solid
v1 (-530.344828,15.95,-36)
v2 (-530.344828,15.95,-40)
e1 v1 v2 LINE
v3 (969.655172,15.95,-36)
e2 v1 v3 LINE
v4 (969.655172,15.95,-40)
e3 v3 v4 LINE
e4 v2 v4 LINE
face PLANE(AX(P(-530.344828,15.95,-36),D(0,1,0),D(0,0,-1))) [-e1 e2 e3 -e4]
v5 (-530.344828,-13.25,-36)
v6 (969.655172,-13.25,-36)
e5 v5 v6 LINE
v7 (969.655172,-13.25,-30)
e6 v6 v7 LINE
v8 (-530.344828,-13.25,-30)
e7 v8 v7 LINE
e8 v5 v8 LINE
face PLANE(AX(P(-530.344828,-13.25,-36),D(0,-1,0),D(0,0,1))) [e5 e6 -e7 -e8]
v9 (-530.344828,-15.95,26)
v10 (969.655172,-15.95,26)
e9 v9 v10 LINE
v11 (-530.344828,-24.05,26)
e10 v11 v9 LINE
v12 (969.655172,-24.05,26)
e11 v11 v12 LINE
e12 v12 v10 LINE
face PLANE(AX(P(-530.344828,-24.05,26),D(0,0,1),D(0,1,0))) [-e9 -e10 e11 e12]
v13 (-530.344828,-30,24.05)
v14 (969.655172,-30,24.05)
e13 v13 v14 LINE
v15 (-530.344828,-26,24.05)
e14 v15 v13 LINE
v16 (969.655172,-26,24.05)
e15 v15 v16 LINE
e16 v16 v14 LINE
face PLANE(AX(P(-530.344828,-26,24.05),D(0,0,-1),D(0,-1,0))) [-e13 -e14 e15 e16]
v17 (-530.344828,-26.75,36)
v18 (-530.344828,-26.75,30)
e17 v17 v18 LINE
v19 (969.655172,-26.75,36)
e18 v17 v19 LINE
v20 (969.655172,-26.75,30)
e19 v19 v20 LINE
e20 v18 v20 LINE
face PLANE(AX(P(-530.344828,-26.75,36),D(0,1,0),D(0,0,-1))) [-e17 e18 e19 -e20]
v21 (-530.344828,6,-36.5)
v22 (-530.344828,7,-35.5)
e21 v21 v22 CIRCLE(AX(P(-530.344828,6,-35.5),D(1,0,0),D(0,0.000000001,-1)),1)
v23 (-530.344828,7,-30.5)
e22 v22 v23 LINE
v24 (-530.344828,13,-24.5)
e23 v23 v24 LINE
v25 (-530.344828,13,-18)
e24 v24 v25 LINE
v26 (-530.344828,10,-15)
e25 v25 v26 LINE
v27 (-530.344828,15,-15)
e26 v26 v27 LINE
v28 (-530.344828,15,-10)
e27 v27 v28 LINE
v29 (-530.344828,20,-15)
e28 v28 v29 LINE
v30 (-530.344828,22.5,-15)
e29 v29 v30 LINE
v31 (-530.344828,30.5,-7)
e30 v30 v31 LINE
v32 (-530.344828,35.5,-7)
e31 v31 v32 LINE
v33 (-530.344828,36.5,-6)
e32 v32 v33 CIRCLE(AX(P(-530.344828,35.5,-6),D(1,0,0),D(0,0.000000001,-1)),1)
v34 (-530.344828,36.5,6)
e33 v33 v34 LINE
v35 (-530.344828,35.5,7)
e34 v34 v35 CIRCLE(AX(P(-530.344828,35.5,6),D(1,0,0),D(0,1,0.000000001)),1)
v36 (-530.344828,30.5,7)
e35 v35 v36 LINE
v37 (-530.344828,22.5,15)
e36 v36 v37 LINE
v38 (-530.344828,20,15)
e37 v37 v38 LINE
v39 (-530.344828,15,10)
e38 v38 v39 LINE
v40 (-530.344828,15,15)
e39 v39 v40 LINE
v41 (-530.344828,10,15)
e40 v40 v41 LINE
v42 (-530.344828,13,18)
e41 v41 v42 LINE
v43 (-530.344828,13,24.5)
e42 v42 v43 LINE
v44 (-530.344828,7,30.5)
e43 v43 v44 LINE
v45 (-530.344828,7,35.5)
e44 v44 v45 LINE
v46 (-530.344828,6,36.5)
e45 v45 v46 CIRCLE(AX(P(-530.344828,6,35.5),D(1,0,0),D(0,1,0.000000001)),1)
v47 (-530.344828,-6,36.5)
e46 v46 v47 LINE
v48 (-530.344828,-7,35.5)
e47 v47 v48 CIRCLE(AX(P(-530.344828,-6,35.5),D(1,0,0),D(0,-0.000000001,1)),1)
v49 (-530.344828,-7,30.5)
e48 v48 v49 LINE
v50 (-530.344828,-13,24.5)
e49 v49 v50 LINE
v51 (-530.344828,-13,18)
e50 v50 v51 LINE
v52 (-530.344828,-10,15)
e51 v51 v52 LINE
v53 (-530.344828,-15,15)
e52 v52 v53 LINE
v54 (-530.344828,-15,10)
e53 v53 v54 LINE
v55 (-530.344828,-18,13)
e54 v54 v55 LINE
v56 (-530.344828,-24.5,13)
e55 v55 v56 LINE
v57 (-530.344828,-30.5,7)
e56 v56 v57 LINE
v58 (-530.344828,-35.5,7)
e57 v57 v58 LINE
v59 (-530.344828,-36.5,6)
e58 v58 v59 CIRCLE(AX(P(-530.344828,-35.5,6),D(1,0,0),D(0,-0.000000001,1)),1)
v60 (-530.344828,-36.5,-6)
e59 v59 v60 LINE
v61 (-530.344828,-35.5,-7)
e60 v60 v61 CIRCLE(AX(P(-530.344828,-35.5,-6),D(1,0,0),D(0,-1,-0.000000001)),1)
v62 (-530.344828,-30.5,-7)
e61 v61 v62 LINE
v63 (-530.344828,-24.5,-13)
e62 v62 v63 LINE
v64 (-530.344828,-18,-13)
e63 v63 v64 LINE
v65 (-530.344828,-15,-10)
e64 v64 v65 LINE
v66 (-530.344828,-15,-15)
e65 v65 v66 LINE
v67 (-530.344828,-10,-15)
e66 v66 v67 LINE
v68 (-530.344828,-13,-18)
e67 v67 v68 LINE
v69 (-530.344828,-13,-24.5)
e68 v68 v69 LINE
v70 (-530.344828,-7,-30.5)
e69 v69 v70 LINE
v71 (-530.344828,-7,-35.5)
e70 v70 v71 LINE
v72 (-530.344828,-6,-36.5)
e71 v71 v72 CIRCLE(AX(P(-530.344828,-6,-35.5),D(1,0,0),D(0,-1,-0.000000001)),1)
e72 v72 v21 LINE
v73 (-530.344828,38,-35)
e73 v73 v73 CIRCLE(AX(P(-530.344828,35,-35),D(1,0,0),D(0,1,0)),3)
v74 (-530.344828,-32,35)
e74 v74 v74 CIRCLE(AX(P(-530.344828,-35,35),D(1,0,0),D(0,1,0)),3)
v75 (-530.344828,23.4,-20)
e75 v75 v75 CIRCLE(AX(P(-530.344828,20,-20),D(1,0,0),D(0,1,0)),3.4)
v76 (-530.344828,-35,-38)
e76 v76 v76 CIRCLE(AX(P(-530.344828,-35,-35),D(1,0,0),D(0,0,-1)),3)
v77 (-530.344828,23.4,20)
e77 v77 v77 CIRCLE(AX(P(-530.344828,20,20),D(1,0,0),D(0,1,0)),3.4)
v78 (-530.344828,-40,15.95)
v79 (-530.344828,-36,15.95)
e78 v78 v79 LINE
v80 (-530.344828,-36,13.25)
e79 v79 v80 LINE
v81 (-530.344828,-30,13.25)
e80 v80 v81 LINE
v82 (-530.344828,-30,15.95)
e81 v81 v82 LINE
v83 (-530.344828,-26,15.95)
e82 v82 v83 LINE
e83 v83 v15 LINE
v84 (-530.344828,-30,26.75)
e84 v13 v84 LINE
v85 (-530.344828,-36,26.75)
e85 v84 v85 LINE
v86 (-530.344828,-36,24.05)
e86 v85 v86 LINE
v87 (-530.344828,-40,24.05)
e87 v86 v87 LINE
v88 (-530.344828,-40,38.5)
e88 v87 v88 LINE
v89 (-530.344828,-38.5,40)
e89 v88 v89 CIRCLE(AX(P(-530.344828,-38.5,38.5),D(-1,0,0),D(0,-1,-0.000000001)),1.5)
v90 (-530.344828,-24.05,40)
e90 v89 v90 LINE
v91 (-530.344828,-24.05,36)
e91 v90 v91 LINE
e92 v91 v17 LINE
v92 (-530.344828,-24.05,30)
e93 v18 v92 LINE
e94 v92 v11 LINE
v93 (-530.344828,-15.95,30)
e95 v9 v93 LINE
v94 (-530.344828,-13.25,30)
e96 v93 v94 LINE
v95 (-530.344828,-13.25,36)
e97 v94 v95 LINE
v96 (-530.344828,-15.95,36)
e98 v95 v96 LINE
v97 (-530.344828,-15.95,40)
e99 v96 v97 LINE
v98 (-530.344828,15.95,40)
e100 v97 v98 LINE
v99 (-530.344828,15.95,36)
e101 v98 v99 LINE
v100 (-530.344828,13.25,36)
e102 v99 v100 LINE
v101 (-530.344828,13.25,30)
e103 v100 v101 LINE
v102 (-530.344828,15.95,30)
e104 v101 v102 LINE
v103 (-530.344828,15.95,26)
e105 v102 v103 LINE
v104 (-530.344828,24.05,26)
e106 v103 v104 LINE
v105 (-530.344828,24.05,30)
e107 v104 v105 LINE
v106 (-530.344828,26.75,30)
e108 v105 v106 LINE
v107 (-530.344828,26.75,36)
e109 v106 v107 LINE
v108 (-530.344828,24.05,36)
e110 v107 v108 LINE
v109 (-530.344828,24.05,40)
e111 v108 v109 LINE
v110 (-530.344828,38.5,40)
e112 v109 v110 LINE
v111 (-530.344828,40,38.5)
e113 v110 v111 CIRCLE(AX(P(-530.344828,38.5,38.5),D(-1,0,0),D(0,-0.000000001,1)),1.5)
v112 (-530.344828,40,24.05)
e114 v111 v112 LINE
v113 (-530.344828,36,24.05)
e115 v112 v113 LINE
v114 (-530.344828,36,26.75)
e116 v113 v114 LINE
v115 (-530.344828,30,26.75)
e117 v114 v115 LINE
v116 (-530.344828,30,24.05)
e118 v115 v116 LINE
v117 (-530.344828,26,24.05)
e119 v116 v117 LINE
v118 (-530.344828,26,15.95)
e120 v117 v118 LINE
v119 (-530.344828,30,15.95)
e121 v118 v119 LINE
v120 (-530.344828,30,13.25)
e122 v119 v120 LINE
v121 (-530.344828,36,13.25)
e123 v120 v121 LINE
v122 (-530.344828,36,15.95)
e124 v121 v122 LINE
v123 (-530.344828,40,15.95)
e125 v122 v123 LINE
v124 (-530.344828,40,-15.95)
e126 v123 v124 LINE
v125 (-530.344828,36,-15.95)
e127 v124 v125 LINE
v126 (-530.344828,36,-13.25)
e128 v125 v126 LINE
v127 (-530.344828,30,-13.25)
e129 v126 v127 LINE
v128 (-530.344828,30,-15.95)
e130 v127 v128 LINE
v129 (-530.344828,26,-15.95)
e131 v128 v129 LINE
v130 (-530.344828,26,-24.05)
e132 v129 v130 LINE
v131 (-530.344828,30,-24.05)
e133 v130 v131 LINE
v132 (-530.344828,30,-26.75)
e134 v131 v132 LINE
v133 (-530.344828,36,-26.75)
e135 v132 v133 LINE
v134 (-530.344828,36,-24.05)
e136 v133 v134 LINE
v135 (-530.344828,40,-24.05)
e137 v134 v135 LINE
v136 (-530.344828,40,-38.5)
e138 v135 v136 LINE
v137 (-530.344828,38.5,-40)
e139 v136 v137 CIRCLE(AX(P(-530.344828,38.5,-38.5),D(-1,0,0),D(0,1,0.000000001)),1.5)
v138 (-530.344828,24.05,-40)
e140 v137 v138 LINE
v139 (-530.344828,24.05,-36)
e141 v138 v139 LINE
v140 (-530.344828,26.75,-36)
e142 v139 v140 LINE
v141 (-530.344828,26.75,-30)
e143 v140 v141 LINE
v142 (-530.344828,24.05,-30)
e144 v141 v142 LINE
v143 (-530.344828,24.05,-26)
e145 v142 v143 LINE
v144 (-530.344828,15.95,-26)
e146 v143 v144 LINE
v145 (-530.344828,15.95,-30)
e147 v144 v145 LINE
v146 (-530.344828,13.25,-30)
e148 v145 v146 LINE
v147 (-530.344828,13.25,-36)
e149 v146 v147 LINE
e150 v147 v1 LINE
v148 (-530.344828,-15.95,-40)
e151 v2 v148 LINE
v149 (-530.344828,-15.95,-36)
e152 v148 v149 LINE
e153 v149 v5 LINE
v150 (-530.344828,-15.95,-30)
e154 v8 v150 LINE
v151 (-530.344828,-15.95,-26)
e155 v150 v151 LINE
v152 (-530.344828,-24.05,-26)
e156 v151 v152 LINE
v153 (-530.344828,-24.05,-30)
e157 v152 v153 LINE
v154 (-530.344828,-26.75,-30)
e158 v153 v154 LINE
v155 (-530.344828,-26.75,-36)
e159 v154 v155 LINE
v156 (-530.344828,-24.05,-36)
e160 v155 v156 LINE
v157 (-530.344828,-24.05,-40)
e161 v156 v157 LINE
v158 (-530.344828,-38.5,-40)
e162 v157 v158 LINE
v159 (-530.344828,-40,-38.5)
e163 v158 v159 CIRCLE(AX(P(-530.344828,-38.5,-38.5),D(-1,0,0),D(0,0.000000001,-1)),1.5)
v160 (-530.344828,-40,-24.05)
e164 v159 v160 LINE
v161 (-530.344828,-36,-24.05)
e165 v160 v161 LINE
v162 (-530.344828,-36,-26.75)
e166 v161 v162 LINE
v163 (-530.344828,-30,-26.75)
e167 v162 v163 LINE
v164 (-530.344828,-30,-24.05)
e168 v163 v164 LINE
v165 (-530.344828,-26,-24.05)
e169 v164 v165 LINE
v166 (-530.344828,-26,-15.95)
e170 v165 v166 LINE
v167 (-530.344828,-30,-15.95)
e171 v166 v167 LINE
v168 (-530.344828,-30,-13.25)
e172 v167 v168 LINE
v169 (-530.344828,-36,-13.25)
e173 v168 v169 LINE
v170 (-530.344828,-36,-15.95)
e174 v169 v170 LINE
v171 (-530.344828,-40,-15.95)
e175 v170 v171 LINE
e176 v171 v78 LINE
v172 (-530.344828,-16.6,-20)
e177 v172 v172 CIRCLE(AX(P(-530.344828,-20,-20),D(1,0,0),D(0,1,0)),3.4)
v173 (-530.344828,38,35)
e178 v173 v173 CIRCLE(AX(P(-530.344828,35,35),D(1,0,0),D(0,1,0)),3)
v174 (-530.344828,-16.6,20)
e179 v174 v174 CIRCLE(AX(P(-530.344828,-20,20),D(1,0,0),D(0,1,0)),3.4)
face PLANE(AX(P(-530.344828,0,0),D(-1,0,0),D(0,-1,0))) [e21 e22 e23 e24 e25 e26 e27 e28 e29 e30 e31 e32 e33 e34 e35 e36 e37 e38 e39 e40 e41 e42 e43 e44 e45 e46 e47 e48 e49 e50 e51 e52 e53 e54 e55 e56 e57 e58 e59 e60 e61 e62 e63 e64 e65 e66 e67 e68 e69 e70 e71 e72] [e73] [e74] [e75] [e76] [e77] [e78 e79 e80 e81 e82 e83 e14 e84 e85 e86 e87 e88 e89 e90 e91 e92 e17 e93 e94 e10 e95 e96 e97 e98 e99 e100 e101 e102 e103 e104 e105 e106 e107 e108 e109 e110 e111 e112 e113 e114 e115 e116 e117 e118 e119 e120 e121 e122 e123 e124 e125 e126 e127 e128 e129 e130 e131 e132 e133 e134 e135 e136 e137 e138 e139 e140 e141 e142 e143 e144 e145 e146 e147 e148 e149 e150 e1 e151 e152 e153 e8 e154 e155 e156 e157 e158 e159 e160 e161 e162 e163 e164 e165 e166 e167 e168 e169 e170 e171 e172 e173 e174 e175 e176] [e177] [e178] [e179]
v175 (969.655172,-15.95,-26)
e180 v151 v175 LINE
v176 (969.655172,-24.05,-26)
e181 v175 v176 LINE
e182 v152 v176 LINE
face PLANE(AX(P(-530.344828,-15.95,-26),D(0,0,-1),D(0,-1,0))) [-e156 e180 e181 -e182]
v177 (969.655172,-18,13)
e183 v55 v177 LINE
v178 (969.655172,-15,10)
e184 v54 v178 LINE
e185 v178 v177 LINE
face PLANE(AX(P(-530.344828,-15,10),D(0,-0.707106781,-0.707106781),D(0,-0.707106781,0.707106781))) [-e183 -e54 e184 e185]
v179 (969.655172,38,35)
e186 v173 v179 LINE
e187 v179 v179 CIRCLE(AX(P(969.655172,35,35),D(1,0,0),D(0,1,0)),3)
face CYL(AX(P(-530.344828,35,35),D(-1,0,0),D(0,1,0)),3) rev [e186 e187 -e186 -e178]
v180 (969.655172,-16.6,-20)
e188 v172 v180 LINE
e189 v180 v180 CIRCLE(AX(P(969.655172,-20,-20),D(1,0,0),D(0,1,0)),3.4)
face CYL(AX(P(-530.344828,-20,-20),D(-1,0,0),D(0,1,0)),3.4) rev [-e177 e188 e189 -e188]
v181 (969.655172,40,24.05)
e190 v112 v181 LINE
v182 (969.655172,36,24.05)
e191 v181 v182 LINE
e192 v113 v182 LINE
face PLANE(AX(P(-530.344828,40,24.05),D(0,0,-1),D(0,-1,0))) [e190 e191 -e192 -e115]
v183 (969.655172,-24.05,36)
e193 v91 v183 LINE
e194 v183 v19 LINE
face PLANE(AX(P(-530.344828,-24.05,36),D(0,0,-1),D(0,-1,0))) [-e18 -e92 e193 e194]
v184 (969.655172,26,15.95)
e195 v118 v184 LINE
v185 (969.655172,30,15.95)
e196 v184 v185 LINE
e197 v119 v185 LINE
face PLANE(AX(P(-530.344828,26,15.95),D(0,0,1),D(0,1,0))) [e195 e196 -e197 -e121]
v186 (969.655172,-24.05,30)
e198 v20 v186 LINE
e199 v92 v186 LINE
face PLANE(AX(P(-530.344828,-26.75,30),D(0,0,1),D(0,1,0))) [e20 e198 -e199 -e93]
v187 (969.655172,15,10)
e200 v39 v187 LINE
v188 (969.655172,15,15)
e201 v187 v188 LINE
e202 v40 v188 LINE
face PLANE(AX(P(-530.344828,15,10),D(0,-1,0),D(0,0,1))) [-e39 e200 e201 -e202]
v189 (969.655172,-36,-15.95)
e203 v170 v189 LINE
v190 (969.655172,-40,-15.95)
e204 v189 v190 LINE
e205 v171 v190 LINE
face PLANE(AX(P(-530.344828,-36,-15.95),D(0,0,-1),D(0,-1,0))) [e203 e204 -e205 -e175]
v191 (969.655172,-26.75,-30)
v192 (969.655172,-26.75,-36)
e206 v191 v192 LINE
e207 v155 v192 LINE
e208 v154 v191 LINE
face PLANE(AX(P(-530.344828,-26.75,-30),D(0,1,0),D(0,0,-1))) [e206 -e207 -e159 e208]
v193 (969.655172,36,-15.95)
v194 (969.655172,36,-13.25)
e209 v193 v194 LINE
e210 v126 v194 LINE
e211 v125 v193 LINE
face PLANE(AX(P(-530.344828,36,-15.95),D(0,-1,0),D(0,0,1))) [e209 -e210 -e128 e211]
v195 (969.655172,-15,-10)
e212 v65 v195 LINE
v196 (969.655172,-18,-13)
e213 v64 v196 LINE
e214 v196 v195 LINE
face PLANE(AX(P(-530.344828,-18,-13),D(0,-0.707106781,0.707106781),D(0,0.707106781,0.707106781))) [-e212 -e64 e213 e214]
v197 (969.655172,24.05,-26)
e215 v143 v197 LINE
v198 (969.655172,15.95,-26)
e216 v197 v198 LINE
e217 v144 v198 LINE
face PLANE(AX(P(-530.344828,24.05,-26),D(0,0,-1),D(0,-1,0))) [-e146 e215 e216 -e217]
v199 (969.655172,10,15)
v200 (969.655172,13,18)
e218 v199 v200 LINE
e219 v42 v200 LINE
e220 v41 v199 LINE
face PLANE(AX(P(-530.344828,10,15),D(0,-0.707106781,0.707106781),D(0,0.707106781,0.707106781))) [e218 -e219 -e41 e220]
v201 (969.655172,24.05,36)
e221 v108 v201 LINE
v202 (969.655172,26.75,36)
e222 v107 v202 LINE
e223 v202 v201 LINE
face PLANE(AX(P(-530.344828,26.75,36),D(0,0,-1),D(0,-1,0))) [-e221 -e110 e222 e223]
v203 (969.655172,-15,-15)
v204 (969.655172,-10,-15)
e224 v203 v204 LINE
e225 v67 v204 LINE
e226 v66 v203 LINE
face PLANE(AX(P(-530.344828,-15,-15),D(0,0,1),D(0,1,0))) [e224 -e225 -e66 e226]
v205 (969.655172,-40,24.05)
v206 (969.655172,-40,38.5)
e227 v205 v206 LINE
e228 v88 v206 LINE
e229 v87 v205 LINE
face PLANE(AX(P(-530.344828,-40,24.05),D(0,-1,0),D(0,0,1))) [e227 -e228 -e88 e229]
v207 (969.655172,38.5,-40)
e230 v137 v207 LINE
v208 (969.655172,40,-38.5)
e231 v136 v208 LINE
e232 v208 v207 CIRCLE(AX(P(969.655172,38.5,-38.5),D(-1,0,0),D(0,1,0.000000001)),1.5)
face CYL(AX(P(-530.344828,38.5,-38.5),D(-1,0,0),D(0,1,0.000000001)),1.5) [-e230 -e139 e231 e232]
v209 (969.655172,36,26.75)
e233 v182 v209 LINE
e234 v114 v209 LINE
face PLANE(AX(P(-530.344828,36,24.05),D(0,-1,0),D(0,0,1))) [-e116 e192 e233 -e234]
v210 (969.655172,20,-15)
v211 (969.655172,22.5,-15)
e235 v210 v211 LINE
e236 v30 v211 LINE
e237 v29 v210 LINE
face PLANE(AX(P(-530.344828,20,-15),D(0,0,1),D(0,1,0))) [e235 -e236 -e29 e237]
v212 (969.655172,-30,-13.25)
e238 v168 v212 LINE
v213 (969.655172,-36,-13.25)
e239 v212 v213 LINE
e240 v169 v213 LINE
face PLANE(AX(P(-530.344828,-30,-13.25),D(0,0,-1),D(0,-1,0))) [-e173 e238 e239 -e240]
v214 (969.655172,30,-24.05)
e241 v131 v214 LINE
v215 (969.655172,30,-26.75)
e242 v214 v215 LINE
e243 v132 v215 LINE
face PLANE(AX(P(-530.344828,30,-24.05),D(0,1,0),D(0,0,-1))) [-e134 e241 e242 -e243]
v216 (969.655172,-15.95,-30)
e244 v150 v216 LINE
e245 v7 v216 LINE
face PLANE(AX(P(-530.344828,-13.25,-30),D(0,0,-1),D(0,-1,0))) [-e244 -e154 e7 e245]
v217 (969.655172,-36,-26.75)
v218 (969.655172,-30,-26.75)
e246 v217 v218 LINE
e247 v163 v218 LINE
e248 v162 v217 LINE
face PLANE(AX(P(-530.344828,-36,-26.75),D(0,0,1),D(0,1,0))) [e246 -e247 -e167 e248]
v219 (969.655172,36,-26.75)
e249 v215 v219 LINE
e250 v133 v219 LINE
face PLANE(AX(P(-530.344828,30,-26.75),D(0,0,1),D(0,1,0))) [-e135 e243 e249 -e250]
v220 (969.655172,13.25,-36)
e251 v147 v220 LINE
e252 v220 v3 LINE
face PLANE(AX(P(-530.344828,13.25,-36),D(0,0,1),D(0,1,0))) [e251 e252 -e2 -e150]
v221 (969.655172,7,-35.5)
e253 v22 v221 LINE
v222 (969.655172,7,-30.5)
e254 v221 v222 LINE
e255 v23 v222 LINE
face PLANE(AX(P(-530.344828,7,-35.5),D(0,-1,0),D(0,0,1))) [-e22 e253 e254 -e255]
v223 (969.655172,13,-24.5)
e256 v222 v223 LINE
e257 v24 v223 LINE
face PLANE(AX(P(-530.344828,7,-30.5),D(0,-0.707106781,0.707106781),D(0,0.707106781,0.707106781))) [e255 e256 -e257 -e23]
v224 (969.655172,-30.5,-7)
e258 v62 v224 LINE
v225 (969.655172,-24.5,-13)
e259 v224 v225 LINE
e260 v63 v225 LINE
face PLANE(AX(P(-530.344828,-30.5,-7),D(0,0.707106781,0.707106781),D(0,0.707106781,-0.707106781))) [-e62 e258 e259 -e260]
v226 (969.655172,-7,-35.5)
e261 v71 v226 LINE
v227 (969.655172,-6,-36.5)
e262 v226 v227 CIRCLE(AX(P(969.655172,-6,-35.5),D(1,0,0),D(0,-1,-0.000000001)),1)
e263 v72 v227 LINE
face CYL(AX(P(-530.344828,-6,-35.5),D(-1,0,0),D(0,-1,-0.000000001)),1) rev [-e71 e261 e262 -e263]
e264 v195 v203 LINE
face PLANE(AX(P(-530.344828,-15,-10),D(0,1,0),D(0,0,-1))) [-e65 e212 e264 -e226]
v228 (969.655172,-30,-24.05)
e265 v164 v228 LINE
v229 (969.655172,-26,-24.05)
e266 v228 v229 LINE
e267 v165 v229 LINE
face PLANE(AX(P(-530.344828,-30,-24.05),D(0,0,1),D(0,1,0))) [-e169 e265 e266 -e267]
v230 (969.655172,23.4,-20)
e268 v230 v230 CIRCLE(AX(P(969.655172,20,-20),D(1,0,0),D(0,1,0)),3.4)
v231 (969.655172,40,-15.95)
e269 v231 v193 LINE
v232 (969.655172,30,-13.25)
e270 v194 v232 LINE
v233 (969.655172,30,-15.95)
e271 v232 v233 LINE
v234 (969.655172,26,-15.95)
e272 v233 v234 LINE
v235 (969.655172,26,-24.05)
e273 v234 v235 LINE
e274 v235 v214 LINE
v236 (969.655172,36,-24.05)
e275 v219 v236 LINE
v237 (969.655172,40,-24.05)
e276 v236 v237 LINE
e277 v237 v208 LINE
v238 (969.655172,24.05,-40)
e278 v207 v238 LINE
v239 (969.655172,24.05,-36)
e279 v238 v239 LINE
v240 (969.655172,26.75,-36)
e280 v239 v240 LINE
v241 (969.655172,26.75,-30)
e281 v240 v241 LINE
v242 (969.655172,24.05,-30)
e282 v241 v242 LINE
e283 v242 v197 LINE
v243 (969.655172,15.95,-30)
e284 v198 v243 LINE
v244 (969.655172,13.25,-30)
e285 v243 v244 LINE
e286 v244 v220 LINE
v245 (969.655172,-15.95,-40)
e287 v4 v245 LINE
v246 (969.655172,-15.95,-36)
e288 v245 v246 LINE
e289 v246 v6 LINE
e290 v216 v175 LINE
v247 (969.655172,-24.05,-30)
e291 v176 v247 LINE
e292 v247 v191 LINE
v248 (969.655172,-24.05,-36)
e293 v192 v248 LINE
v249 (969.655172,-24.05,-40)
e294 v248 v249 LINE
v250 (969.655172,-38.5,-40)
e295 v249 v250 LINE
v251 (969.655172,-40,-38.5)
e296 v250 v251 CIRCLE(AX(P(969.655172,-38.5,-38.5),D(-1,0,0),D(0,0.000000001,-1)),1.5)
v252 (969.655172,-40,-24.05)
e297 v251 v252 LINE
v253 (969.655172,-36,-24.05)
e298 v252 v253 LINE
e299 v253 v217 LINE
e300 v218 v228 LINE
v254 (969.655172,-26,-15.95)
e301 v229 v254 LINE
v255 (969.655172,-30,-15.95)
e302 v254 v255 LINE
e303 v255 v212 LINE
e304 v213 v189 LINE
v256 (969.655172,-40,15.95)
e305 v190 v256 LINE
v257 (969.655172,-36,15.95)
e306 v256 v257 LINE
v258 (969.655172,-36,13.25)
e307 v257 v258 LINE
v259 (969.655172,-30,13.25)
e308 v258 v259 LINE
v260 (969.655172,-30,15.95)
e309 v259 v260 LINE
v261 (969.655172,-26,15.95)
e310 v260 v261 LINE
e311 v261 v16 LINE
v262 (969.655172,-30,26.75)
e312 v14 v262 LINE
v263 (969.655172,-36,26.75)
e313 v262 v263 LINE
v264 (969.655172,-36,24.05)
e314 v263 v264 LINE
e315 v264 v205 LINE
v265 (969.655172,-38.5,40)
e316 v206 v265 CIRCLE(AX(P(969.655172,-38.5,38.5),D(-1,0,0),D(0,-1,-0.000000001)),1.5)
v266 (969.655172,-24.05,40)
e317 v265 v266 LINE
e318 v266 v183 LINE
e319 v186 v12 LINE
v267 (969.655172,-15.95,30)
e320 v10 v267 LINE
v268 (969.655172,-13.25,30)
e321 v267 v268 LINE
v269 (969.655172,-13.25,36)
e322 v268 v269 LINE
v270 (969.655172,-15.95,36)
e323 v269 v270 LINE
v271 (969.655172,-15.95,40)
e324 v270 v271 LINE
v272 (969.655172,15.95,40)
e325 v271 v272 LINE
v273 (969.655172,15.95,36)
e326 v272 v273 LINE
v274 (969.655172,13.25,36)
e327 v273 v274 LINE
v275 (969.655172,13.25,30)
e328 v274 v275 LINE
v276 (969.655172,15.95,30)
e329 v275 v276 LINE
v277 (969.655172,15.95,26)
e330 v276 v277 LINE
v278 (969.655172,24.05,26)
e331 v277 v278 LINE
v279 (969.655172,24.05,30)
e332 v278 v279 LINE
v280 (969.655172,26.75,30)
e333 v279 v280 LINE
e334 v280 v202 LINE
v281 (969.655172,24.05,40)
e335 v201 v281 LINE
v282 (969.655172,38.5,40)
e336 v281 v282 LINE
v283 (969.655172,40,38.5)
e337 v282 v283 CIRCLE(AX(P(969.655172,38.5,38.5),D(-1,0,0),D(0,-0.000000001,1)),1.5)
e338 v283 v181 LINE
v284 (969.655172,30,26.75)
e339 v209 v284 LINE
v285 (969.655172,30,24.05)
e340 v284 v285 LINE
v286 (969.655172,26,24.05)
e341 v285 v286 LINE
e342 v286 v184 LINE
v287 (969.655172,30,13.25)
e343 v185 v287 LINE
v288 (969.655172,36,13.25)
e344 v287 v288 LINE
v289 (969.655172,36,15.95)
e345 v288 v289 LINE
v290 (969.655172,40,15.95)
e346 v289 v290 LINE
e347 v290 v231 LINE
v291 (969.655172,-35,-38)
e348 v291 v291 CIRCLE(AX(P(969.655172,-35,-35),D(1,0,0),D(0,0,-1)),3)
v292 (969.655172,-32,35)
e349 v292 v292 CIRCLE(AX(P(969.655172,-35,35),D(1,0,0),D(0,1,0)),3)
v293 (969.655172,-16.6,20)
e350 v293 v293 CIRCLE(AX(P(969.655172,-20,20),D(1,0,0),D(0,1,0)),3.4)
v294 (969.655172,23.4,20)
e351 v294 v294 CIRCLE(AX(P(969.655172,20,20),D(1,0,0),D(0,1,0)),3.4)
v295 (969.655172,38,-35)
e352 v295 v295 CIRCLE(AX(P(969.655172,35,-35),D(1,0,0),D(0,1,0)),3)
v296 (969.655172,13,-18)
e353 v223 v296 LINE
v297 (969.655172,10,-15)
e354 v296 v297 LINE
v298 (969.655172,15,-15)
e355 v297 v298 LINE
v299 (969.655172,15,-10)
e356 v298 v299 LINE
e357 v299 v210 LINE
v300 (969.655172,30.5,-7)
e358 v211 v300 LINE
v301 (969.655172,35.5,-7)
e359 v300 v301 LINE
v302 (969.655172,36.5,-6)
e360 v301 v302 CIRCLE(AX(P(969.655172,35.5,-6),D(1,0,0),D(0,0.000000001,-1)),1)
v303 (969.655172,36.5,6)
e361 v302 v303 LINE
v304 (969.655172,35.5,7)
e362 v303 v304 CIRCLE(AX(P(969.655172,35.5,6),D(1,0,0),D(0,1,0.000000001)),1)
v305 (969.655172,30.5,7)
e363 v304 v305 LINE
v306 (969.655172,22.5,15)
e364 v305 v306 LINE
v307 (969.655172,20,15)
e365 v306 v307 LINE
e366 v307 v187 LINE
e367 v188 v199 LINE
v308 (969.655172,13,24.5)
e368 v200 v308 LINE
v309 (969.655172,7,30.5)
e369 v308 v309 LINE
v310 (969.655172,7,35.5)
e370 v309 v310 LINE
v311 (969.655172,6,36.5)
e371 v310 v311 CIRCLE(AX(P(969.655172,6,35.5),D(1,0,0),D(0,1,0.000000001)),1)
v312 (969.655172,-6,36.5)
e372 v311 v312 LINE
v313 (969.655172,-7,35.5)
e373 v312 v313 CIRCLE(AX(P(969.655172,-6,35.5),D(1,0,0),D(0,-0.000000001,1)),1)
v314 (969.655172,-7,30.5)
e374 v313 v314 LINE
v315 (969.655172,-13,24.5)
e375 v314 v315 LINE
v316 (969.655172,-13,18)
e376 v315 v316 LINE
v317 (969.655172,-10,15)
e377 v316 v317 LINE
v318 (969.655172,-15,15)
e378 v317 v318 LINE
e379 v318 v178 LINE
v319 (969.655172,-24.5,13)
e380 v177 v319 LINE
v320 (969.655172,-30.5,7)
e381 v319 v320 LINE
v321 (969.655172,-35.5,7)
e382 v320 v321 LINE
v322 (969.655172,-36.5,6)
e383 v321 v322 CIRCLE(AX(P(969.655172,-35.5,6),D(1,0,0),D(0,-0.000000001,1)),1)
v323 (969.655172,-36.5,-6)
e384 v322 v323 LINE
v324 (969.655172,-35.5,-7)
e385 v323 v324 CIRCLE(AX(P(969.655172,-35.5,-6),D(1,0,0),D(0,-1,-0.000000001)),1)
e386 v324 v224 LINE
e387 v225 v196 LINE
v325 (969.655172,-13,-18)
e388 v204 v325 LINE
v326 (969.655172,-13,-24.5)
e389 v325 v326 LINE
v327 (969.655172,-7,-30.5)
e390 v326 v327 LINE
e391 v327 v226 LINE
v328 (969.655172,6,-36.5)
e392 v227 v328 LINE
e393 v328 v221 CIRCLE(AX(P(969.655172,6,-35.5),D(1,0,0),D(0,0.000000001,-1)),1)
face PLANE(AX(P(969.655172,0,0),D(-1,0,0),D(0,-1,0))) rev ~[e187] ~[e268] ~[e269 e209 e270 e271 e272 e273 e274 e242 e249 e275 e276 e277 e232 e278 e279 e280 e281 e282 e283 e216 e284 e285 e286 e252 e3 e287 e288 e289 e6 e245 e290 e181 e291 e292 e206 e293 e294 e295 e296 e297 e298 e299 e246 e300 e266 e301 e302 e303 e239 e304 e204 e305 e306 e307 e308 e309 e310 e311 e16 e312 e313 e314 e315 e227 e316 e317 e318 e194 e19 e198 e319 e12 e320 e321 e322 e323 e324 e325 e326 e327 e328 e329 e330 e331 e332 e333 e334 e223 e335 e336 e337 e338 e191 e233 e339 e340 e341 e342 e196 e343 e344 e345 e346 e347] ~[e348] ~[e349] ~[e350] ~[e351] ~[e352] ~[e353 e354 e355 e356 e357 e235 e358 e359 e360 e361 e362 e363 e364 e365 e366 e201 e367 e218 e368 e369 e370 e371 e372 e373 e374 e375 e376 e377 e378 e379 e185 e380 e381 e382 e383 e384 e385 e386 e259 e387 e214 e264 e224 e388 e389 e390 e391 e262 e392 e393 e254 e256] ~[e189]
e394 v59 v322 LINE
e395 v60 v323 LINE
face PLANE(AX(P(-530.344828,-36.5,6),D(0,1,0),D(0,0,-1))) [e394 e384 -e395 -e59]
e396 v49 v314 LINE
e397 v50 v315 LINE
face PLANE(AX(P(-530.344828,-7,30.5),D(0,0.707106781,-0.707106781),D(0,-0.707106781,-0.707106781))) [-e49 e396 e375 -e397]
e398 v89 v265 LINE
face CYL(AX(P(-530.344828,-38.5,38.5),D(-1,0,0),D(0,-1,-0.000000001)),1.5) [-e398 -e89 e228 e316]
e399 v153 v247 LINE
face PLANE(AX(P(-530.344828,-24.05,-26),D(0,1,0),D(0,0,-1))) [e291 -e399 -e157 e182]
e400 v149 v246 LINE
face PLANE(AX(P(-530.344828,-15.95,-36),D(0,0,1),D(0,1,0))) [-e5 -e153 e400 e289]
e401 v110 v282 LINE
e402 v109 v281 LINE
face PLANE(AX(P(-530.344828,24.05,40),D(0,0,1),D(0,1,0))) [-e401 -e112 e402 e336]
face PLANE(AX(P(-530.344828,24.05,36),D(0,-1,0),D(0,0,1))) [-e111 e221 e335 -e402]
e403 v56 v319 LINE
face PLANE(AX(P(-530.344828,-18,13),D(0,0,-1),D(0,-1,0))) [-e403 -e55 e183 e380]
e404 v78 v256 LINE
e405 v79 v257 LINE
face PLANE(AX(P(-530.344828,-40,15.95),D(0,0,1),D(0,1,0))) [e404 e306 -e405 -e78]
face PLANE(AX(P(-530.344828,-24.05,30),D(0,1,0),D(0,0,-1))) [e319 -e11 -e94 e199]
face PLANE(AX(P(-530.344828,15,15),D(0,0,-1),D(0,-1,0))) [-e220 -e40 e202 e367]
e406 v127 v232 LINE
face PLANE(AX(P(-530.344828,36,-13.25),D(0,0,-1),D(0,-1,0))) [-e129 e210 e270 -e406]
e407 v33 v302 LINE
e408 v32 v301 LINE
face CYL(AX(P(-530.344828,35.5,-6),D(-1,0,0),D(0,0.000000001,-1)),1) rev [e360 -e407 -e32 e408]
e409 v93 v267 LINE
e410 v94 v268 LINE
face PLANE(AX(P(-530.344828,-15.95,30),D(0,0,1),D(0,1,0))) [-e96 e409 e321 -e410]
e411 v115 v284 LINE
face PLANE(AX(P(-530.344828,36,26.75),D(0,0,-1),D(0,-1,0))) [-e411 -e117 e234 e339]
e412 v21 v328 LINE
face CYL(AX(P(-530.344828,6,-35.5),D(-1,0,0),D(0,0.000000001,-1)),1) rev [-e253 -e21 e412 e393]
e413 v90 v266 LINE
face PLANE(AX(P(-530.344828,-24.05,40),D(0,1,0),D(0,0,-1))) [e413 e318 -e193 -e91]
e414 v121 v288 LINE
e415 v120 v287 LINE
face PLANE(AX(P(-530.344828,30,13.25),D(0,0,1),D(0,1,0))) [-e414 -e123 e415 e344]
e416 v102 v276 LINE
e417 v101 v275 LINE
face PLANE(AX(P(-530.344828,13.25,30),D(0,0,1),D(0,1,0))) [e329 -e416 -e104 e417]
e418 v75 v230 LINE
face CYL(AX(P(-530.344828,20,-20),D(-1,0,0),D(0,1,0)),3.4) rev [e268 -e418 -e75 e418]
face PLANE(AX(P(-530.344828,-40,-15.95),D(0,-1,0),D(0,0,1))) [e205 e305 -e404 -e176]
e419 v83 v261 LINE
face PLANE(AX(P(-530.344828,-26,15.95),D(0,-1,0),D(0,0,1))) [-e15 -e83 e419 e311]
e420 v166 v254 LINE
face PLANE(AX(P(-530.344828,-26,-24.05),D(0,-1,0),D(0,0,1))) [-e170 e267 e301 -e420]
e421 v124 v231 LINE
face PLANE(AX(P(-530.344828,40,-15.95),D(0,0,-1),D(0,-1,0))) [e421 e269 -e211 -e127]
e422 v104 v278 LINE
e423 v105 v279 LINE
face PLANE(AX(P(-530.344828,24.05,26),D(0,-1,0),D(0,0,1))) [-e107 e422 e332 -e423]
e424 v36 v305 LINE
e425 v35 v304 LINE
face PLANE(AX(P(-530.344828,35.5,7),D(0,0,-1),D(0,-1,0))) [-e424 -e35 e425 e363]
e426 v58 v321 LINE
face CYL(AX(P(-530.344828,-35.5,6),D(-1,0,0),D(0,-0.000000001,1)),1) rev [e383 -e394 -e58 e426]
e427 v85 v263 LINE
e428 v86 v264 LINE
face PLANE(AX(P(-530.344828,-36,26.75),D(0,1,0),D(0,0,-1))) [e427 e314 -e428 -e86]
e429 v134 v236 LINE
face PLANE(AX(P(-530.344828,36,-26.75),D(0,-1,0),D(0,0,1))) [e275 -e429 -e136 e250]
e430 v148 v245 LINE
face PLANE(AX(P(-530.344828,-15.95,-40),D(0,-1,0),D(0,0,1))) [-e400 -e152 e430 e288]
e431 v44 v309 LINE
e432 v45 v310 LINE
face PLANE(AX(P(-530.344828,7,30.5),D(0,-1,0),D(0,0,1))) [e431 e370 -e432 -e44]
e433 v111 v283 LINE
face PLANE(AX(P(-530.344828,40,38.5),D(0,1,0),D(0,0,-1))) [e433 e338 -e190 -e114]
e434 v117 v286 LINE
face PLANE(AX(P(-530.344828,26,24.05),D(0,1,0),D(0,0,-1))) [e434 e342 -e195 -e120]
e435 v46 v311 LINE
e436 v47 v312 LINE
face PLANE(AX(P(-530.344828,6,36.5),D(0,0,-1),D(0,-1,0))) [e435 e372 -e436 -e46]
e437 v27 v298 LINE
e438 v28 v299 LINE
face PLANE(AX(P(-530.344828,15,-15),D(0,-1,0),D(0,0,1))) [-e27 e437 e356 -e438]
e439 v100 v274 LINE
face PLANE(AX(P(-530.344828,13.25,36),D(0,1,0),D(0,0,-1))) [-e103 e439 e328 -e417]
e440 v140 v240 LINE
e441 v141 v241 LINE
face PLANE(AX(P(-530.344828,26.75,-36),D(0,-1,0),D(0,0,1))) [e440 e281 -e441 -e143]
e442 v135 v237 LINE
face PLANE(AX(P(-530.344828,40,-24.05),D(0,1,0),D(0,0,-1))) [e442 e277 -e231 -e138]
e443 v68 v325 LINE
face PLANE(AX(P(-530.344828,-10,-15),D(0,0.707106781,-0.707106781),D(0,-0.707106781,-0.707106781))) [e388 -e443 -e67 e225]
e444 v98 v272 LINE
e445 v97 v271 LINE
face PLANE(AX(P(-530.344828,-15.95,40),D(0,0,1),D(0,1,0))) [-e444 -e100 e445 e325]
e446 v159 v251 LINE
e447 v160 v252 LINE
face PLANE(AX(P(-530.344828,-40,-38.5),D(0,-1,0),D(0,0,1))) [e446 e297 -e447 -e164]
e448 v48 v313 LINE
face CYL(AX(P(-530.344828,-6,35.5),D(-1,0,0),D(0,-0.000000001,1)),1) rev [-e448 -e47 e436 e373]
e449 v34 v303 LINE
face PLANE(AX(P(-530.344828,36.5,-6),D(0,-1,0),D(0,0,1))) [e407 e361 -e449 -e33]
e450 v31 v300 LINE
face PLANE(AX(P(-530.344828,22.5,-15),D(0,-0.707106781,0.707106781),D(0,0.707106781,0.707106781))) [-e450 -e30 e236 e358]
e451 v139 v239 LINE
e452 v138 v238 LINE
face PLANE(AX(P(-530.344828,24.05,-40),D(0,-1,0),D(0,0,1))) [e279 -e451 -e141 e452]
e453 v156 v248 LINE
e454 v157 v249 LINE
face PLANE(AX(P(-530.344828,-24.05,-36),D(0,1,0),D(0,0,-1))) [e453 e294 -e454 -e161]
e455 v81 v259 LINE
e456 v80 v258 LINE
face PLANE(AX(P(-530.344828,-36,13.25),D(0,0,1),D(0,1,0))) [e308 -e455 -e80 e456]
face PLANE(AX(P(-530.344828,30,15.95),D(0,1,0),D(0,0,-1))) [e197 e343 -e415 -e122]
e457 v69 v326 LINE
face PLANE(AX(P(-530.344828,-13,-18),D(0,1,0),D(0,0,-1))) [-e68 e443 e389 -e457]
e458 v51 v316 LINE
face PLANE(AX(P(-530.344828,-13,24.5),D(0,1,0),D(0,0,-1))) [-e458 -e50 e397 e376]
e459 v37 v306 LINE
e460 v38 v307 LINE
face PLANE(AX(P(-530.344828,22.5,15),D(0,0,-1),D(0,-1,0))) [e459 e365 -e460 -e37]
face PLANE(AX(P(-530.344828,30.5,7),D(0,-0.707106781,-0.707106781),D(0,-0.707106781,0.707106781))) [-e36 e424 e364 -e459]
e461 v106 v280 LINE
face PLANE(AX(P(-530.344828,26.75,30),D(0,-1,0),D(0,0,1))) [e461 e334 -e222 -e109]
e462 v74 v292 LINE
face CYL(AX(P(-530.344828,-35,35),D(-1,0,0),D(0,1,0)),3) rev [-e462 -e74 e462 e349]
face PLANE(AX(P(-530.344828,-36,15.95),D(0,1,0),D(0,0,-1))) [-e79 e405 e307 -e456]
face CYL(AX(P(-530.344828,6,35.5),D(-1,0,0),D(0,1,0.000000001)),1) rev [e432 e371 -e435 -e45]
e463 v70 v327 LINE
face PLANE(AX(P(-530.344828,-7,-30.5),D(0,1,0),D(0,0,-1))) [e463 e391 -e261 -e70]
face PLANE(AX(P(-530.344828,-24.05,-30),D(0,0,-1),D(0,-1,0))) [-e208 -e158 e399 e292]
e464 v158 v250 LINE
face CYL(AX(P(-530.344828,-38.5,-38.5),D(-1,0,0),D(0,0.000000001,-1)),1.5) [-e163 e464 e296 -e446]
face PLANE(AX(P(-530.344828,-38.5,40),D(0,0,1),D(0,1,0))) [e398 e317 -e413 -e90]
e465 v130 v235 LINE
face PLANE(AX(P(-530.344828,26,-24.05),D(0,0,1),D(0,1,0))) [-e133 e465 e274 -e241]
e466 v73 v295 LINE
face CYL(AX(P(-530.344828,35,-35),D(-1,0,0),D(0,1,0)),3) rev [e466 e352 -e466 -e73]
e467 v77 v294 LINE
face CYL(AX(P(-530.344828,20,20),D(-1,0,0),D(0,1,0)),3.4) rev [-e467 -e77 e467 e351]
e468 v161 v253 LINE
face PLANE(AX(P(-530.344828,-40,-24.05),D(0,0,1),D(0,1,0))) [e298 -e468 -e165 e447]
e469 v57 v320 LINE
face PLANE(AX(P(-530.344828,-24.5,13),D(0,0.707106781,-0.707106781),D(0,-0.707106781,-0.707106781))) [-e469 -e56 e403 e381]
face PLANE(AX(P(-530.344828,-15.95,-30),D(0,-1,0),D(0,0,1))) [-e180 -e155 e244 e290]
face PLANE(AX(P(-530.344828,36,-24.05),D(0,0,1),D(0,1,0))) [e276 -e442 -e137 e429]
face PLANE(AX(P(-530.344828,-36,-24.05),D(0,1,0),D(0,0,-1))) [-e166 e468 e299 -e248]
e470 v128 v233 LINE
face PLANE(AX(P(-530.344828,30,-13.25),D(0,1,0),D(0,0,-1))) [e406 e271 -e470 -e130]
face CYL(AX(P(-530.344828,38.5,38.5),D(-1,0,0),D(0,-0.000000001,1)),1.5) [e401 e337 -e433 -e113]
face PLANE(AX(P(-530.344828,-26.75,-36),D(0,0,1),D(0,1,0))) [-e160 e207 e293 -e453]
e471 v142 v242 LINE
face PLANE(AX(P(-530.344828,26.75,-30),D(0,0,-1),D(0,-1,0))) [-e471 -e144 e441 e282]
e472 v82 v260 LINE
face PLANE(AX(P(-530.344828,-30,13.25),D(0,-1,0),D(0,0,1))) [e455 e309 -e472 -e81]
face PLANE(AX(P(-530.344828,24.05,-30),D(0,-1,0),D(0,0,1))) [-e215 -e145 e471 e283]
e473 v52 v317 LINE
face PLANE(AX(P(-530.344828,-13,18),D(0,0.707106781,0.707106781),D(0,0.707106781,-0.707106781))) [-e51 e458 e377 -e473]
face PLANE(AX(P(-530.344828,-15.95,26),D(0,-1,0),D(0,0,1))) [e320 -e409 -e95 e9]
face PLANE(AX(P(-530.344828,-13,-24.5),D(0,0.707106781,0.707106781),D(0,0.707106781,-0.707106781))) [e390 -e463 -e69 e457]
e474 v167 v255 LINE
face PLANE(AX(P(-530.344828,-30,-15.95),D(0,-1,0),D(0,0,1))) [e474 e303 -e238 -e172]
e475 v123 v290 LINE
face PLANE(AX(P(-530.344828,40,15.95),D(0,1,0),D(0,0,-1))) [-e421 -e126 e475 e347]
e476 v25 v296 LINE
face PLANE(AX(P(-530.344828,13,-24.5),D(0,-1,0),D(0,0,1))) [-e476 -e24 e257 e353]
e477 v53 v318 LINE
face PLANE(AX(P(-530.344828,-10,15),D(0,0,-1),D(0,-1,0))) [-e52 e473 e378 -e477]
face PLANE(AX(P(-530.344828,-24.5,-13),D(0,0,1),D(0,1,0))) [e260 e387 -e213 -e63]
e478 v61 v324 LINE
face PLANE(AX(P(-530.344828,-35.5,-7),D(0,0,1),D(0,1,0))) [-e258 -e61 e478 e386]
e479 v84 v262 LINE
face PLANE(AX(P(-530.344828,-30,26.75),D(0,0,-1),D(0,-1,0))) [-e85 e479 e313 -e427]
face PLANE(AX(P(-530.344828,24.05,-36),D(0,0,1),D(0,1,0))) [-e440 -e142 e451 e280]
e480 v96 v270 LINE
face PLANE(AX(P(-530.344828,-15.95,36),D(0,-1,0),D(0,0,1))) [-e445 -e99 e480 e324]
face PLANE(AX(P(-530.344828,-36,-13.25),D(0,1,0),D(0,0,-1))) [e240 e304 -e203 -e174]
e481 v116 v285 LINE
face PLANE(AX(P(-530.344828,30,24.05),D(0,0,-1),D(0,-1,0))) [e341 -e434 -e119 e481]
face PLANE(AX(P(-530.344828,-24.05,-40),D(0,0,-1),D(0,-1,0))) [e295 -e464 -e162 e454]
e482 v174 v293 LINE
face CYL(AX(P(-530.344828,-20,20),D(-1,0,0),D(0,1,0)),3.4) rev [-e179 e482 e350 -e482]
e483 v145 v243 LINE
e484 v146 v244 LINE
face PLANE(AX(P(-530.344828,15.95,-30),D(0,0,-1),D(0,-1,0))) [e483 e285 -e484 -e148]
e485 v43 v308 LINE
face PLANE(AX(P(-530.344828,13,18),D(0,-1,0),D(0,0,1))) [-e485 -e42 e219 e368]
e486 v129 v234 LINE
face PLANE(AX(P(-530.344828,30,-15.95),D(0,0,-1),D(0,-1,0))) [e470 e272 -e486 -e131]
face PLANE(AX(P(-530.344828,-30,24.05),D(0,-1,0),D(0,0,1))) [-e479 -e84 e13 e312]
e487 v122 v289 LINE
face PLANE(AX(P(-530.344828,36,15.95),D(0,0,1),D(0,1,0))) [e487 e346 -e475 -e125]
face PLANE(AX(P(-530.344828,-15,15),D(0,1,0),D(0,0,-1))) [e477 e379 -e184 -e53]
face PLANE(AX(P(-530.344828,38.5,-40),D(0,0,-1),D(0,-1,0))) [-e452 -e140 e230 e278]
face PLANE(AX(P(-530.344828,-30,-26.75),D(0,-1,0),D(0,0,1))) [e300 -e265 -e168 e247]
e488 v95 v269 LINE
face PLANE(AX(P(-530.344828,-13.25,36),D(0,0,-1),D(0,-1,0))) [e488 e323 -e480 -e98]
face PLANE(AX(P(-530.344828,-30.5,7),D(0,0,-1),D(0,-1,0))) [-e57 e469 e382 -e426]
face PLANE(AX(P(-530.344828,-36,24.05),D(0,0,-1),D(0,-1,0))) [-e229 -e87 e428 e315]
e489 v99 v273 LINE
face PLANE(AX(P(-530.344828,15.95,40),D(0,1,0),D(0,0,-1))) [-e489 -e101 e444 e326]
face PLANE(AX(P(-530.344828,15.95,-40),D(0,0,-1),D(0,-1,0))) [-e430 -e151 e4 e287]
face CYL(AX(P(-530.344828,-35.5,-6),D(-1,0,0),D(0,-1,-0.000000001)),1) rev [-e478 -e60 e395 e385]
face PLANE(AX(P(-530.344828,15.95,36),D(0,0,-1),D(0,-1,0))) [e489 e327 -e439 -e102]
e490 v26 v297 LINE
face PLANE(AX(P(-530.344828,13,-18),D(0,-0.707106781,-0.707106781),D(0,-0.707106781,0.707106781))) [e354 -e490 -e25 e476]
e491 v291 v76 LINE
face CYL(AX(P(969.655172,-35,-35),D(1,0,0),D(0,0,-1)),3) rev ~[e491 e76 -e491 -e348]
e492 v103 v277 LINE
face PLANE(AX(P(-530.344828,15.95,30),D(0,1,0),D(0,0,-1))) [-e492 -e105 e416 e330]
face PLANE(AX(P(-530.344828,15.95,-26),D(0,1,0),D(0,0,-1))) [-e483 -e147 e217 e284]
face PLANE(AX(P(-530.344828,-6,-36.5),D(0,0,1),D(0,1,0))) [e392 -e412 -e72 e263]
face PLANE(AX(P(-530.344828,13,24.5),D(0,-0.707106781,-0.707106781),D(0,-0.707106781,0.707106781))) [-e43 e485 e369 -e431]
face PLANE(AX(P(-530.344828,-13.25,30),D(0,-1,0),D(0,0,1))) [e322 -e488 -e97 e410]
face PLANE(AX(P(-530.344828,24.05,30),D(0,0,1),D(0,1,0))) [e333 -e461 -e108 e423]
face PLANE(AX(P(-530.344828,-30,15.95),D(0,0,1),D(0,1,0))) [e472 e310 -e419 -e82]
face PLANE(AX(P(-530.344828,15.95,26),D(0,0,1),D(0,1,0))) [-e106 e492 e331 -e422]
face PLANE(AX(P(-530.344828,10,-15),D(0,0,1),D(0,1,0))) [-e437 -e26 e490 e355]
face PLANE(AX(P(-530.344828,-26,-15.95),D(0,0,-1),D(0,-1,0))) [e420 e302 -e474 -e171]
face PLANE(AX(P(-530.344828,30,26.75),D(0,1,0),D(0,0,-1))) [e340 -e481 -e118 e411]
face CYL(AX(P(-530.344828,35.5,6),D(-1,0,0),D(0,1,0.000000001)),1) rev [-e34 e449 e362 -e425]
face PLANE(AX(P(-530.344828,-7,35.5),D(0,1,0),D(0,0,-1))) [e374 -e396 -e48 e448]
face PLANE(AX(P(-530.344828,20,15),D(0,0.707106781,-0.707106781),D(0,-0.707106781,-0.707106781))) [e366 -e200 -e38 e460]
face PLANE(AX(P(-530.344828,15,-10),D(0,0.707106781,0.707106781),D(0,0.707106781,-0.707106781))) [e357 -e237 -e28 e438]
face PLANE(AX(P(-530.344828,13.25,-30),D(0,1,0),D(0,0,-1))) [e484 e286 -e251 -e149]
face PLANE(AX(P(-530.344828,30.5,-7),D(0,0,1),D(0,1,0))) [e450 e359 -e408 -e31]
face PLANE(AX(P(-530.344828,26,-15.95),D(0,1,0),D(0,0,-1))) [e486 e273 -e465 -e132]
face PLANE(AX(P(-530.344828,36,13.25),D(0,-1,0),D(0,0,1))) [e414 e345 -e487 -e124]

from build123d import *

# Parameters (mm, degrees)
SKETCH1_R                                 = 3.4
SKETCH1_R_2                               = 3
ALUMINIUM_PROFILE_80_X_80G_X_R1_5_1_DEPTH = 1500
SKETCH10_R                                = 3
CUT_EXTRUDE1_DEPTH                        = 1502.066287677


with BuildPart() as part:
    # Sketch1 → Aluminium profile 80 X 80G X R1.5(1) (new body)
    with BuildSketch(Plane.YZ.offset(-530.344827586)):
        with BuildLine():
            Line((-24.05, 40), (-24.05, 36))
            Line((-24.05, 36), (-26.75, 36))
            Line((-26.75, 36), (-26.75, 30))
            Line((-26.75, 30), (-24.05, 30))
            Line((-24.05, 30), (-24.05, 26))
            Line((-24.05, 26), (-15.95, 26))
            Line((-15.95, 26), (-15.95, 30))
            Line((-15.95, 30), (-13.25, 30))
            Line((-13.25, 30), (-13.25, 36))
            Line((-13.25, 36), (-15.95, 36))
            Line((-15.95, 36), (-15.95, 40))
            Line((-15.95, 40), (15.95, 40))
            Line((15.95, 40), (15.95, 36))
            Line((15.95, 36), (13.25, 36))
            Line((13.25, 36), (13.25, 30))
            Line((13.25, 30), (15.95, 30))
            Line((15.95, 30), (15.95, 26))
            Line((15.95, 26), (24.05, 26))
            Line((24.05, 26), (24.05, 30))
            Line((24.05, 30), (26.75, 30))
            Line((26.75, 30), (26.75, 36))
            Line((26.75, 36), (24.05, 36))
            Line((24.05, 36), (24.05, 40))
            Line((24.05, 40), (38.5, 40))
            ThreePointArc((38.5, 40), (39.560660172, 39.560660172), (40, 38.5))
            Line((40, 38.5), (40, 24.05))
            Line((40, 24.05), (36, 24.05))
            Line((36, 24.05), (36, 26.75))
            Line((36, 26.75), (30, 26.75))
            Line((30, 26.75), (30, 24.05))
            Line((30, 24.05), (26, 24.05))
            Line((26, 24.05), (26, 15.95))
            Line((26, 15.95), (30, 15.95))
            Line((30, 15.95), (30, 13.25))
            Line((30, 13.25), (36, 13.25))
            Line((36, 13.25), (36, 15.95))
            Line((36, 15.95), (40, 15.95))
            Line((40, 15.95), (40, -15.95))
            Line((40, -15.95), (36, -15.95))
            Line((36, -15.95), (36, -13.25))
            Line((36, -13.25), (30, -13.25))
            Line((30, -13.25), (30, -15.95))
            Line((30, -15.95), (26, -15.95))
            Line((26, -15.95), (26, -24.05))
            Line((26, -24.05), (30, -24.05))
            Line((30, -24.05), (30, -26.75))
            Line((30, -26.75), (36, -26.75))
            Line((36, -26.75), (36, -24.05))
            Line((36, -24.05), (40, -24.05))
            Line((40, -24.05), (40, -38.5))
            ThreePointArc((40, -38.5), (39.560660172, -39.560660172), (38.5, -40))
            Line((38.5, -40), (24.05, -40))
            Line((24.05, -40), (24.05, -36))
            Line((24.05, -36), (26.75, -36))
            Line((26.75, -36), (26.75, -30))
            Line((26.75, -30), (24.05, -30))
            Line((24.05, -30), (24.05, -26))
            Line((24.05, -26), (15.95, -26))
            Line((15.95, -26), (15.95, -30))
            Line((15.95, -30), (13.25, -30))
            Line((13.25, -30), (13.25, -36))
            Line((13.25, -36), (15.95, -36))
            Line((15.95, -36), (15.95, -40))
            Line((15.95, -40), (-15.95, -40))
            Line((-15.95, -40), (-15.95, -36))
            Line((-15.95, -36), (-13.25, -36))
            Line((-13.25, -36), (-13.25, -30))
            Line((-13.25, -30), (-15.95, -30))
            Line((-15.95, -30), (-15.95, -26))
            Line((-15.95, -26), (-24.05, -26))
            Line((-24.05, -26), (-24.05, -30))
            Line((-24.05, -30), (-26.75, -30))
            Line((-26.75, -30), (-26.75, -36))
            Line((-26.75, -36), (-24.05, -36))
            Line((-24.05, -36), (-24.05, -40))
            Line((-24.05, -40), (-38.5, -40))
            ThreePointArc((-38.5, -40), (-39.560660172, -39.560660172), (-40, -38.5))
            Line((-40, -38.5), (-40, -24.05))
            Line((-40, -24.05), (-36, -24.05))
            Line((-36, -24.05), (-36, -26.75))
            Line((-36, -26.75), (-30, -26.75))
            Line((-30, -26.75), (-30, -24.05))
            Line((-30, -24.05), (-26, -24.05))
            Line((-26, -24.05), (-26, -15.95))
            Line((-26, -15.95), (-30, -15.95))
            Line((-30, -15.95), (-30, -13.25))
            Line((-30, -13.25), (-36, -13.25))
            Line((-36, -13.25), (-36, -15.95))
            Line((-36, -15.95), (-40, -15.95))
            Line((-40, -15.95), (-40, 15.95))
            Line((-40, 15.95), (-36, 15.95))
            Line((-36, 15.95), (-36, 13.25))
            Line((-36, 13.25), (-30, 13.25))
            Line((-30, 13.25), (-30, 15.95))
            Line((-30, 15.95), (-26, 15.95))
            Line((-26, 15.95), (-26, 24.05))
            Line((-26, 24.05), (-30, 24.05))
            Line((-30, 24.05), (-30, 26.75))
            Line((-30, 26.75), (-36, 26.75))
            Line((-36, 26.75), (-36, 24.05))
            Line((-36, 24.05), (-40, 24.05))
            Line((-40, 24.05), (-40, 38.5))
            ThreePointArc((-40, 38.5), (-39.560660172, 39.560660172), (-38.5, 40))
            Line((-38.5, 40), (-24.05, 40))
        make_face()
        with Locations((-20, 20)):
            Circle(SKETCH1_R, mode=Mode.SUBTRACT)
        with Locations((20, 20)):
            Circle(SKETCH1_R, mode=Mode.SUBTRACT)
        with Locations((20, -20)):
            Circle(SKETCH1_R, mode=Mode.SUBTRACT)
        with Locations((-20, -20)):
            Circle(SKETCH1_R, mode=Mode.SUBTRACT)
        with Locations((-35, 35)):
            Circle(SKETCH1_R_2, mode=Mode.SUBTRACT)
        with Locations((35, 35)):
            Circle(SKETCH1_R_2, mode=Mode.SUBTRACT)
        with Locations((35, -35)):
            Circle(SKETCH1_R_2, mode=Mode.SUBTRACT)
        with BuildLine():
            Line((-13, 18), (-10, 15))
            Line((-10, 15), (-15, 15))
            Line((-15, 15), (-15, 10))
            Line((-15, 10), (-18, 13))
            Line((-18, 13), (-24.5, 13))
            Line((-24.5, 13), (-30.5, 7))
            Line((-30.5, 7), (-35.5, 7))
            ThreePointArc((-35.5, 7), (-36.207106781, 6.707106781), (-36.5, 6))
            Line((-36.5, 6), (-36.5, -6))
            ThreePointArc((-36.5, -6), (-36.207106781, -6.707106781), (-35.5, -7))
            Line((-35.5, -7), (-30.5, -7))
            Line((-30.5, -7), (-24.5, -13))
            Line((-24.5, -13), (-18, -13))
            Line((-18, -13), (-15, -10))
            Line((-15, -10), (-15, -15))
            Line((-15, -15), (-10, -15))
            Line((-10, -15), (-13, -18))
            Line((-13, -18), (-13, -24.5))
            Line((-13, -24.5), (-7, -30.5))
            Line((-7, -30.5), (-7, -35.5))
            ThreePointArc((-7, -35.5), (-6.707106781, -36.207106781), (-6, -36.5))
            Line((-6, -36.5), (6, -36.5))
            ThreePointArc((6, -36.5), (6.707106781, -36.207106781), (7, -35.5))
            Line((7, -35.5), (7, -30.5))
            Line((7, -30.5), (13, -24.5))
            Line((13, -24.5), (13, -18))
            Line((13, -18), (10, -15))
            Line((10, -15), (15, -15))
            Line((15, -15), (15, -10))
            Line((15, -10), (20, -15))
            Line((20, -15), (22.5, -15))
            Line((22.5, -15), (30.5, -7))
            Line((30.5, -7), (35.5, -7))
            ThreePointArc((35.5, -7), (36.207106781, -6.707106781), (36.5, -6))
            Line((36.5, -6), (36.5, 6))
            ThreePointArc((36.5, 6), (36.207106781, 6.707106781), (35.5, 7))
            Line((35.5, 7), (30.5, 7))
            Line((30.5, 7), (22.5, 15))
            Line((22.5, 15), (20, 15))
            Line((20, 15), (15, 10))
            Line((15, 10), (15, 15))
            Line((15, 15), (10, 15))
            Line((10, 15), (13, 18))
            Line((13, 18), (13, 24.5))
            Line((13, 24.5), (7, 30.5))
            Line((7, 30.5), (7, 35.5))
            ThreePointArc((7, 35.5), (6.707106781, 36.207106781), (6, 36.5))
            Line((6, 36.5), (-6, 36.5))
            ThreePointArc((-6, 36.5), (-6.707106781, 36.207106781), (-7, 35.5))
            Line((-7, 35.5), (-7, 30.5))
            Line((-7, 30.5), (-13, 24.5))
            Line((-13, 24.5), (-13, 18))
        make_face(mode=Mode.SUBTRACT)
    extrude(amount=ALUMINIUM_PROFILE_80_X_80G_X_R1_5_1_DEPTH)

    # Sketch10 → Cut-Extrude1 (cut, through all)
    with BuildSketch(Plane(origin=(969.655172414, 0, 0), x_dir=(0, 0, -1), z_dir=(1, 0, 0))):
        with Locations((35, -35)):
            Circle(SKETCH10_R)
    extrude(amount=-CUT_EXTRUDE1_DEPTH, mode=Mode.SUBTRACT)


solid = part.part
